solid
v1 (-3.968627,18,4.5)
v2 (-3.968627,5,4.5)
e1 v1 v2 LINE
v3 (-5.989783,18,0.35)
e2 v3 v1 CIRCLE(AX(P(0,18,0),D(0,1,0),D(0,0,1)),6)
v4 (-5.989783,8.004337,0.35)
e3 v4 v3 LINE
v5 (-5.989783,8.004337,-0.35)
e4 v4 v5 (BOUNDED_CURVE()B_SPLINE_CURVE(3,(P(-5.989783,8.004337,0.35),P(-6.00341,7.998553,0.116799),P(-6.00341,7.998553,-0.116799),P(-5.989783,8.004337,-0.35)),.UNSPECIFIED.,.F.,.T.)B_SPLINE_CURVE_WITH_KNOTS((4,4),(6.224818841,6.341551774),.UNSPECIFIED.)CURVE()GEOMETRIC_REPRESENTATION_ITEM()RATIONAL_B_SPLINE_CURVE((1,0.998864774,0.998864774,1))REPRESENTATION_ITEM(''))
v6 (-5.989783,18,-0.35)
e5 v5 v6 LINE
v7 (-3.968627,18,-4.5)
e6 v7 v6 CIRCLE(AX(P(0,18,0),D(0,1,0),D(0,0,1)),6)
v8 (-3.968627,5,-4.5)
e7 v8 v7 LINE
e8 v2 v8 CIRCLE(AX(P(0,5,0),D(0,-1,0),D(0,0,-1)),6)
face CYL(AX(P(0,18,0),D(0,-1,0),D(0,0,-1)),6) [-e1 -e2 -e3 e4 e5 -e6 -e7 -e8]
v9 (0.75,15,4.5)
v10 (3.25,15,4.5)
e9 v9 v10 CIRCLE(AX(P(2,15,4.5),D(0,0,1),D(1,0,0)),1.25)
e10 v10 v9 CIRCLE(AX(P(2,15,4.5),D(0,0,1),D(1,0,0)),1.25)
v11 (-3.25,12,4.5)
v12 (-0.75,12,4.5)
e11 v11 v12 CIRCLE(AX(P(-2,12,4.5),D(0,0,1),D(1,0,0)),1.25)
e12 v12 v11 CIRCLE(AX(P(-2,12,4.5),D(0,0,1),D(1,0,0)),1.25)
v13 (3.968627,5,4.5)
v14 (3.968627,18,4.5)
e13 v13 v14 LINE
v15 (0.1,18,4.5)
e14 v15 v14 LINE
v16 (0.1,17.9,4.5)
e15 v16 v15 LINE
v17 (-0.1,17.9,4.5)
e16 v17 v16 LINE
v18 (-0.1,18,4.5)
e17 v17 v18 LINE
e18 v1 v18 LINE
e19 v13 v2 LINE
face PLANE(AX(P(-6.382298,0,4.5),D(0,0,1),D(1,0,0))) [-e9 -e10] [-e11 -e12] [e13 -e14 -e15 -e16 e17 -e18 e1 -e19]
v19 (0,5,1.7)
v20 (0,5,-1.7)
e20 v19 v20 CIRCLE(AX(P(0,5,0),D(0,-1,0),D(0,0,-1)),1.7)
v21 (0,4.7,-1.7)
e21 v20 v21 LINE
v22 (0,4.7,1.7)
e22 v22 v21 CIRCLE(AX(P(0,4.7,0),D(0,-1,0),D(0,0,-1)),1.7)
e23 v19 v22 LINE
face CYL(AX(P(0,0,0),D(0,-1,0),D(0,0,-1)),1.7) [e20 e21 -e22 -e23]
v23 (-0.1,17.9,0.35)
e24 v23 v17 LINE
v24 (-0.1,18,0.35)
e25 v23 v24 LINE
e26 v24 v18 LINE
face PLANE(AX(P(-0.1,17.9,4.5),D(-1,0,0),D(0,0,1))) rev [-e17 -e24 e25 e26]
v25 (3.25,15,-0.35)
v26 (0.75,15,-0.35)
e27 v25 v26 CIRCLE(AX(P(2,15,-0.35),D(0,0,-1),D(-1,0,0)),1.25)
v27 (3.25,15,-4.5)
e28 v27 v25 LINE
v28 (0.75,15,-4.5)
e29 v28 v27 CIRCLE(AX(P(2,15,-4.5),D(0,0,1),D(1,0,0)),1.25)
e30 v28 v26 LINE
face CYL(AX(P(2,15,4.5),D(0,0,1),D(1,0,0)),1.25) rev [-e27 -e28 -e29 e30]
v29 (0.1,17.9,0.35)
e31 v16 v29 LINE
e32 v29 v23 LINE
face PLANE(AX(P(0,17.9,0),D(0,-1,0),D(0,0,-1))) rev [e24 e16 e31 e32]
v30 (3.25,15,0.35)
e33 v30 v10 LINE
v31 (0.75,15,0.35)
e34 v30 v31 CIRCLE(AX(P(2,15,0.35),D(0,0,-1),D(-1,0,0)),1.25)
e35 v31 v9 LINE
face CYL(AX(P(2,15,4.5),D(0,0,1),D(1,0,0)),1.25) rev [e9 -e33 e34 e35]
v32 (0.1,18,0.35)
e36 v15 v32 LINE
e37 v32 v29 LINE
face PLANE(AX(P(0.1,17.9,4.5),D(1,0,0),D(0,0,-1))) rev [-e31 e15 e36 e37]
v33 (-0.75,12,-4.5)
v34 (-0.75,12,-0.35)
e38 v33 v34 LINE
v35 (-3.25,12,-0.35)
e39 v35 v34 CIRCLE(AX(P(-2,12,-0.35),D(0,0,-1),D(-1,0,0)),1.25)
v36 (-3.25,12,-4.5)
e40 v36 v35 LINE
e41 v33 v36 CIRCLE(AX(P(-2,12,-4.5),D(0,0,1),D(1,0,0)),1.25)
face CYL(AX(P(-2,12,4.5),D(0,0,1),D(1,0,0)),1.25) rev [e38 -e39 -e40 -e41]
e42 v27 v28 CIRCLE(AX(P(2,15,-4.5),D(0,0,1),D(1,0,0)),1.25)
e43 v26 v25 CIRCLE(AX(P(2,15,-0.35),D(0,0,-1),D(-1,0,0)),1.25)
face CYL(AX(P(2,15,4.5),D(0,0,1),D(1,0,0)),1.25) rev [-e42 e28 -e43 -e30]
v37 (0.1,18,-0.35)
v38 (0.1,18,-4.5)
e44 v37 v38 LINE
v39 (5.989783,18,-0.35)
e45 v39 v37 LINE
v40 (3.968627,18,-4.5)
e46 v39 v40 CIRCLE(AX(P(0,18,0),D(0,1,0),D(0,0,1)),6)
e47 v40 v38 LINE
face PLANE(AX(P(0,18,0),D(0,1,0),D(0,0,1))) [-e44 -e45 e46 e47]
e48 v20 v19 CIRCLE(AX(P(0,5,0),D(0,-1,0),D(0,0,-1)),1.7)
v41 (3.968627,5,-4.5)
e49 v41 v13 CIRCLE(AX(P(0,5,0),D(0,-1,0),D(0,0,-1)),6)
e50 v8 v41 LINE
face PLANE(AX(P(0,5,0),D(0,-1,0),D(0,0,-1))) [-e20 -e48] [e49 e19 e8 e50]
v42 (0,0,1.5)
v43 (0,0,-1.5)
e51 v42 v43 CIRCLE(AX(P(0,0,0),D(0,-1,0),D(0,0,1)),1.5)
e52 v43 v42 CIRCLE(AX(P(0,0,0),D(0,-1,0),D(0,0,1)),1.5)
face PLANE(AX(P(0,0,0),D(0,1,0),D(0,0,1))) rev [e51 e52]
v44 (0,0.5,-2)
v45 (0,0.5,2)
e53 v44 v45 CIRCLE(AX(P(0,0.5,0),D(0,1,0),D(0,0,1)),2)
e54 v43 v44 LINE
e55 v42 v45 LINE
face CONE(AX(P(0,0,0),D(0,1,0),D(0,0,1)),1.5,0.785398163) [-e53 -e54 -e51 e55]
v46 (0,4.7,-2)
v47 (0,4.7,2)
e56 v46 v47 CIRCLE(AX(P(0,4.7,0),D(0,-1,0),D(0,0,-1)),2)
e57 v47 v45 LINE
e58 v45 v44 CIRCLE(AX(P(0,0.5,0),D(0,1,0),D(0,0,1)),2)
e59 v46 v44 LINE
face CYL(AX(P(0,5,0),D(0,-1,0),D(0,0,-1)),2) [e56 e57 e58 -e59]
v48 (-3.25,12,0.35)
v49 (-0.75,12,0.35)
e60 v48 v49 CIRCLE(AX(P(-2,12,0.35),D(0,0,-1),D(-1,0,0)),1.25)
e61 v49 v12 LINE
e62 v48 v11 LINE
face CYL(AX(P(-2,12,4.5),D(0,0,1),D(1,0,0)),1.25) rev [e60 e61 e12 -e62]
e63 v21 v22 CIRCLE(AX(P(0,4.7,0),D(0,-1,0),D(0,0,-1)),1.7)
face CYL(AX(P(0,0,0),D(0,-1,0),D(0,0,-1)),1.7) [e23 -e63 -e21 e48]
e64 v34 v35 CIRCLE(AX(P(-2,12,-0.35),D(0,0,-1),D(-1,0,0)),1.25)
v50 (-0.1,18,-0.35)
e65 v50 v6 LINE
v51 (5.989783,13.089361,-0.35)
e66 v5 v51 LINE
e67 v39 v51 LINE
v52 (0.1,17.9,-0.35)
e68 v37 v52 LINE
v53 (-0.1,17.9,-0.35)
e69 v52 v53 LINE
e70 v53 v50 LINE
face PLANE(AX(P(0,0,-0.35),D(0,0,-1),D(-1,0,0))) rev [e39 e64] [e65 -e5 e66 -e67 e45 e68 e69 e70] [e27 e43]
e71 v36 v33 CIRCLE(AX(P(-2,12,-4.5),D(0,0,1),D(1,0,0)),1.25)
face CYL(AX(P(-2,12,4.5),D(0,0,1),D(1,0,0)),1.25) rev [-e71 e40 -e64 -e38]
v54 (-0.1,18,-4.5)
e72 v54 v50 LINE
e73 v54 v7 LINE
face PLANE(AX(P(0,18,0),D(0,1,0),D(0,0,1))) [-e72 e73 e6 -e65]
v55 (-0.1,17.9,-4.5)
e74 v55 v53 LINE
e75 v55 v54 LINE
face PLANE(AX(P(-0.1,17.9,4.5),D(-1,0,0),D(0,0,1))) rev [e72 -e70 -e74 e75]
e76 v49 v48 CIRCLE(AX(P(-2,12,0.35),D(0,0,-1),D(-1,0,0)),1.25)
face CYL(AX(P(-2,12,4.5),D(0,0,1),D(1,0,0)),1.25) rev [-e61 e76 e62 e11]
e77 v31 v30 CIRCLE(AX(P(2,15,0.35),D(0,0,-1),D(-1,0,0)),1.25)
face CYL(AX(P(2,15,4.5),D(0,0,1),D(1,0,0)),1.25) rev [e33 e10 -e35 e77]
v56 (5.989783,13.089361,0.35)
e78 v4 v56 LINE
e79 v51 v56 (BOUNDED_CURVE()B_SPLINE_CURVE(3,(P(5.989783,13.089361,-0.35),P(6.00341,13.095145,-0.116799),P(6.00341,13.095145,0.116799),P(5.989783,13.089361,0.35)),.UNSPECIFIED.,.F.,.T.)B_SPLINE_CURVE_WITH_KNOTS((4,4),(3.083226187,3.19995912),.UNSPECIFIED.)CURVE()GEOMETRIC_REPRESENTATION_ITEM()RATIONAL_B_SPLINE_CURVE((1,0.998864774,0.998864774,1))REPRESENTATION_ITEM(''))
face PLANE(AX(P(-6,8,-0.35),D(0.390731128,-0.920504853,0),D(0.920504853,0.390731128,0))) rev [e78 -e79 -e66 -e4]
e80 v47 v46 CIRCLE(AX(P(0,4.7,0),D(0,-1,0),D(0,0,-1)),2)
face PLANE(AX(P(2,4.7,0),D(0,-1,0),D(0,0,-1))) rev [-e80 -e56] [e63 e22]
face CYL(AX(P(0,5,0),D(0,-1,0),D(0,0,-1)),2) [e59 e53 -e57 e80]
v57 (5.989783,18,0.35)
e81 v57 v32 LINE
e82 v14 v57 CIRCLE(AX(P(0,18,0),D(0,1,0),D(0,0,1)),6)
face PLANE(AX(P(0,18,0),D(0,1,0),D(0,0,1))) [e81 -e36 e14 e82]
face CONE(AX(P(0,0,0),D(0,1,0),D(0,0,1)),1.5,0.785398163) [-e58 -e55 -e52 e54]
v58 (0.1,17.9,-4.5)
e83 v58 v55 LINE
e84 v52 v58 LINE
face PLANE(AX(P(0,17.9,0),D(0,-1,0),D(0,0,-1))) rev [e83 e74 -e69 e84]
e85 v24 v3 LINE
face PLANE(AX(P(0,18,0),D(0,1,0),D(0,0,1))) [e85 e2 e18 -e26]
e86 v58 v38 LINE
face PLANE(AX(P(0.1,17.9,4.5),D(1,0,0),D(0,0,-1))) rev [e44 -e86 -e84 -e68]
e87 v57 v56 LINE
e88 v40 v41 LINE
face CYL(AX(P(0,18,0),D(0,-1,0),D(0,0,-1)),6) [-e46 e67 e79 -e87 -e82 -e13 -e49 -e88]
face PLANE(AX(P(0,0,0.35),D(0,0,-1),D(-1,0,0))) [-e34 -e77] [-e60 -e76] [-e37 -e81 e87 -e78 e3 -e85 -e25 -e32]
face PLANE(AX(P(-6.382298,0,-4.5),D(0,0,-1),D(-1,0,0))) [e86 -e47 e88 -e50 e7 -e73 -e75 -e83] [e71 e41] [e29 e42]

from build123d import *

# Parameters (mm, degrees)
SKETCH1_R           = 6
BOSS_EXTRUDE1_DEPTH = 18
SKETCH2_OUTSIDE_W   = 18.948
SKETCH2_OUTSIDE_H   = 18.948
SKETCH2_OUTSIDE_R   = 2
CUT_EXTRUDE1_DEPTH  = 5
CUT_EXTRUDE2_DEPTH  = 0.35
CHAMFER1_SIZE       = 0.5
SKETCH6_W           = 0.3
SKETCH6_H           = 0.3
SKETCH9_OUTSIDE_W   = 18.948
SKETCH9_OUTSIDE_H   = 18.948
SKETCH9_OUTSIDE_W_2 = 12.764596016
SKETCH9_OUTSIDE_H_2 = 9
CUT_EXTRUDE3_DEPTH  = 20.899748742
M3_TAPPED_HOLE1_D   = 2.5
SKETCH14_W          = 0.2
SKETCH14_H          = 9
CUT_EXTRUDE5_DEPTH  = 0.1


with BuildPart() as part:
    # Sketch1 → Boss-Extrude1 (new body)
    with BuildSketch(Plane(origin=(0, 0, 0), x_dir=(1, 0, 0), z_dir=(0, 1, 0))):
        with Locations(Location((0, 0, 0), (0, 0, 270))):
            Circle(SKETCH1_R)
    extrude(amount=BOSS_EXTRUDE1_DEPTH)

    # Sketch2 outside → Cut-Extrude1 (cut)
    with BuildSketch(Plane.XZ):
        Rectangle(SKETCH2_OUTSIDE_W, SKETCH2_OUTSIDE_H)
        with Locations(Location((0, 0, 0), (0, 0, 270))):
            Circle(SKETCH2_OUTSIDE_R, mode=Mode.SUBTRACT)
    extrude(amount=-CUT_EXTRUDE1_DEPTH, mode=Mode.SUBTRACT)

    # Sketch8 → Cut-Extrude2 (cut, symmetric)
    with BuildSketch(Plane.XY):
        Polygon((-6, 8), (6, 13.093697795), (6, 18), (-6, 18), align=None)
    extrude(amount=CUT_EXTRUDE2_DEPTH, both=True, mode=Mode.SUBTRACT)

    # Chamfer1
    chamfer1_edges = [part.edges().sort_by_distance(p)[0] for p in [
        (0, 0, 2),
    ]]
    chamfer(chamfer1_edges, length=CHAMFER1_SIZE)

    # Sketch6 → Cut-Revolve1 (revolve, cut)
    with BuildSketch(Plane.XY, mode=Mode.PRIVATE) as cut_revolve1_sk:
        with Locations((1.85, 4.85)):
            Rectangle(SKETCH6_W, SKETCH6_H)
    revolve(cut_revolve1_sk.sketch.rotate(Axis((0, 0, 0), (0, 1, 0)), 90), axis=Axis((0, 0, 0), (0, 1, 0)), mode=Mode.SUBTRACT)

    # Sketch9 outside → Cut-Extrude3 (cut, through all)
    with BuildSketch(Plane(origin=(0, 18, 0), x_dir=(1, 0, 0), z_dir=(0, 1, 0))):
        Rectangle(SKETCH9_OUTSIDE_W, SKETCH9_OUTSIDE_H)
        Rectangle(SKETCH9_OUTSIDE_W_2, SKETCH9_OUTSIDE_H_2, mode=Mode.SUBTRACT)
    extrude(amount=-CUT_EXTRUDE3_DEPTH, mode=Mode.SUBTRACT)

    # M3 Tapped Hole1 (through all)
    with Locations(Plane.XY.offset(4.5)):
        with Locations((2, 15), (-2, 12)):
            Hole(M3_TAPPED_HOLE1_D / 2)

    # Sketch14 → Cut-Extrude5 (cut)
    with BuildSketch(Plane(origin=(0, 18, 0), x_dir=(1, 0, 0), z_dir=(0, 1, 0))):
        Rectangle(SKETCH14_W, SKETCH14_H)
    extrude(amount=-CUT_EXTRUDE5_DEPTH, mode=Mode.SUBTRACT)


solid = part.part
